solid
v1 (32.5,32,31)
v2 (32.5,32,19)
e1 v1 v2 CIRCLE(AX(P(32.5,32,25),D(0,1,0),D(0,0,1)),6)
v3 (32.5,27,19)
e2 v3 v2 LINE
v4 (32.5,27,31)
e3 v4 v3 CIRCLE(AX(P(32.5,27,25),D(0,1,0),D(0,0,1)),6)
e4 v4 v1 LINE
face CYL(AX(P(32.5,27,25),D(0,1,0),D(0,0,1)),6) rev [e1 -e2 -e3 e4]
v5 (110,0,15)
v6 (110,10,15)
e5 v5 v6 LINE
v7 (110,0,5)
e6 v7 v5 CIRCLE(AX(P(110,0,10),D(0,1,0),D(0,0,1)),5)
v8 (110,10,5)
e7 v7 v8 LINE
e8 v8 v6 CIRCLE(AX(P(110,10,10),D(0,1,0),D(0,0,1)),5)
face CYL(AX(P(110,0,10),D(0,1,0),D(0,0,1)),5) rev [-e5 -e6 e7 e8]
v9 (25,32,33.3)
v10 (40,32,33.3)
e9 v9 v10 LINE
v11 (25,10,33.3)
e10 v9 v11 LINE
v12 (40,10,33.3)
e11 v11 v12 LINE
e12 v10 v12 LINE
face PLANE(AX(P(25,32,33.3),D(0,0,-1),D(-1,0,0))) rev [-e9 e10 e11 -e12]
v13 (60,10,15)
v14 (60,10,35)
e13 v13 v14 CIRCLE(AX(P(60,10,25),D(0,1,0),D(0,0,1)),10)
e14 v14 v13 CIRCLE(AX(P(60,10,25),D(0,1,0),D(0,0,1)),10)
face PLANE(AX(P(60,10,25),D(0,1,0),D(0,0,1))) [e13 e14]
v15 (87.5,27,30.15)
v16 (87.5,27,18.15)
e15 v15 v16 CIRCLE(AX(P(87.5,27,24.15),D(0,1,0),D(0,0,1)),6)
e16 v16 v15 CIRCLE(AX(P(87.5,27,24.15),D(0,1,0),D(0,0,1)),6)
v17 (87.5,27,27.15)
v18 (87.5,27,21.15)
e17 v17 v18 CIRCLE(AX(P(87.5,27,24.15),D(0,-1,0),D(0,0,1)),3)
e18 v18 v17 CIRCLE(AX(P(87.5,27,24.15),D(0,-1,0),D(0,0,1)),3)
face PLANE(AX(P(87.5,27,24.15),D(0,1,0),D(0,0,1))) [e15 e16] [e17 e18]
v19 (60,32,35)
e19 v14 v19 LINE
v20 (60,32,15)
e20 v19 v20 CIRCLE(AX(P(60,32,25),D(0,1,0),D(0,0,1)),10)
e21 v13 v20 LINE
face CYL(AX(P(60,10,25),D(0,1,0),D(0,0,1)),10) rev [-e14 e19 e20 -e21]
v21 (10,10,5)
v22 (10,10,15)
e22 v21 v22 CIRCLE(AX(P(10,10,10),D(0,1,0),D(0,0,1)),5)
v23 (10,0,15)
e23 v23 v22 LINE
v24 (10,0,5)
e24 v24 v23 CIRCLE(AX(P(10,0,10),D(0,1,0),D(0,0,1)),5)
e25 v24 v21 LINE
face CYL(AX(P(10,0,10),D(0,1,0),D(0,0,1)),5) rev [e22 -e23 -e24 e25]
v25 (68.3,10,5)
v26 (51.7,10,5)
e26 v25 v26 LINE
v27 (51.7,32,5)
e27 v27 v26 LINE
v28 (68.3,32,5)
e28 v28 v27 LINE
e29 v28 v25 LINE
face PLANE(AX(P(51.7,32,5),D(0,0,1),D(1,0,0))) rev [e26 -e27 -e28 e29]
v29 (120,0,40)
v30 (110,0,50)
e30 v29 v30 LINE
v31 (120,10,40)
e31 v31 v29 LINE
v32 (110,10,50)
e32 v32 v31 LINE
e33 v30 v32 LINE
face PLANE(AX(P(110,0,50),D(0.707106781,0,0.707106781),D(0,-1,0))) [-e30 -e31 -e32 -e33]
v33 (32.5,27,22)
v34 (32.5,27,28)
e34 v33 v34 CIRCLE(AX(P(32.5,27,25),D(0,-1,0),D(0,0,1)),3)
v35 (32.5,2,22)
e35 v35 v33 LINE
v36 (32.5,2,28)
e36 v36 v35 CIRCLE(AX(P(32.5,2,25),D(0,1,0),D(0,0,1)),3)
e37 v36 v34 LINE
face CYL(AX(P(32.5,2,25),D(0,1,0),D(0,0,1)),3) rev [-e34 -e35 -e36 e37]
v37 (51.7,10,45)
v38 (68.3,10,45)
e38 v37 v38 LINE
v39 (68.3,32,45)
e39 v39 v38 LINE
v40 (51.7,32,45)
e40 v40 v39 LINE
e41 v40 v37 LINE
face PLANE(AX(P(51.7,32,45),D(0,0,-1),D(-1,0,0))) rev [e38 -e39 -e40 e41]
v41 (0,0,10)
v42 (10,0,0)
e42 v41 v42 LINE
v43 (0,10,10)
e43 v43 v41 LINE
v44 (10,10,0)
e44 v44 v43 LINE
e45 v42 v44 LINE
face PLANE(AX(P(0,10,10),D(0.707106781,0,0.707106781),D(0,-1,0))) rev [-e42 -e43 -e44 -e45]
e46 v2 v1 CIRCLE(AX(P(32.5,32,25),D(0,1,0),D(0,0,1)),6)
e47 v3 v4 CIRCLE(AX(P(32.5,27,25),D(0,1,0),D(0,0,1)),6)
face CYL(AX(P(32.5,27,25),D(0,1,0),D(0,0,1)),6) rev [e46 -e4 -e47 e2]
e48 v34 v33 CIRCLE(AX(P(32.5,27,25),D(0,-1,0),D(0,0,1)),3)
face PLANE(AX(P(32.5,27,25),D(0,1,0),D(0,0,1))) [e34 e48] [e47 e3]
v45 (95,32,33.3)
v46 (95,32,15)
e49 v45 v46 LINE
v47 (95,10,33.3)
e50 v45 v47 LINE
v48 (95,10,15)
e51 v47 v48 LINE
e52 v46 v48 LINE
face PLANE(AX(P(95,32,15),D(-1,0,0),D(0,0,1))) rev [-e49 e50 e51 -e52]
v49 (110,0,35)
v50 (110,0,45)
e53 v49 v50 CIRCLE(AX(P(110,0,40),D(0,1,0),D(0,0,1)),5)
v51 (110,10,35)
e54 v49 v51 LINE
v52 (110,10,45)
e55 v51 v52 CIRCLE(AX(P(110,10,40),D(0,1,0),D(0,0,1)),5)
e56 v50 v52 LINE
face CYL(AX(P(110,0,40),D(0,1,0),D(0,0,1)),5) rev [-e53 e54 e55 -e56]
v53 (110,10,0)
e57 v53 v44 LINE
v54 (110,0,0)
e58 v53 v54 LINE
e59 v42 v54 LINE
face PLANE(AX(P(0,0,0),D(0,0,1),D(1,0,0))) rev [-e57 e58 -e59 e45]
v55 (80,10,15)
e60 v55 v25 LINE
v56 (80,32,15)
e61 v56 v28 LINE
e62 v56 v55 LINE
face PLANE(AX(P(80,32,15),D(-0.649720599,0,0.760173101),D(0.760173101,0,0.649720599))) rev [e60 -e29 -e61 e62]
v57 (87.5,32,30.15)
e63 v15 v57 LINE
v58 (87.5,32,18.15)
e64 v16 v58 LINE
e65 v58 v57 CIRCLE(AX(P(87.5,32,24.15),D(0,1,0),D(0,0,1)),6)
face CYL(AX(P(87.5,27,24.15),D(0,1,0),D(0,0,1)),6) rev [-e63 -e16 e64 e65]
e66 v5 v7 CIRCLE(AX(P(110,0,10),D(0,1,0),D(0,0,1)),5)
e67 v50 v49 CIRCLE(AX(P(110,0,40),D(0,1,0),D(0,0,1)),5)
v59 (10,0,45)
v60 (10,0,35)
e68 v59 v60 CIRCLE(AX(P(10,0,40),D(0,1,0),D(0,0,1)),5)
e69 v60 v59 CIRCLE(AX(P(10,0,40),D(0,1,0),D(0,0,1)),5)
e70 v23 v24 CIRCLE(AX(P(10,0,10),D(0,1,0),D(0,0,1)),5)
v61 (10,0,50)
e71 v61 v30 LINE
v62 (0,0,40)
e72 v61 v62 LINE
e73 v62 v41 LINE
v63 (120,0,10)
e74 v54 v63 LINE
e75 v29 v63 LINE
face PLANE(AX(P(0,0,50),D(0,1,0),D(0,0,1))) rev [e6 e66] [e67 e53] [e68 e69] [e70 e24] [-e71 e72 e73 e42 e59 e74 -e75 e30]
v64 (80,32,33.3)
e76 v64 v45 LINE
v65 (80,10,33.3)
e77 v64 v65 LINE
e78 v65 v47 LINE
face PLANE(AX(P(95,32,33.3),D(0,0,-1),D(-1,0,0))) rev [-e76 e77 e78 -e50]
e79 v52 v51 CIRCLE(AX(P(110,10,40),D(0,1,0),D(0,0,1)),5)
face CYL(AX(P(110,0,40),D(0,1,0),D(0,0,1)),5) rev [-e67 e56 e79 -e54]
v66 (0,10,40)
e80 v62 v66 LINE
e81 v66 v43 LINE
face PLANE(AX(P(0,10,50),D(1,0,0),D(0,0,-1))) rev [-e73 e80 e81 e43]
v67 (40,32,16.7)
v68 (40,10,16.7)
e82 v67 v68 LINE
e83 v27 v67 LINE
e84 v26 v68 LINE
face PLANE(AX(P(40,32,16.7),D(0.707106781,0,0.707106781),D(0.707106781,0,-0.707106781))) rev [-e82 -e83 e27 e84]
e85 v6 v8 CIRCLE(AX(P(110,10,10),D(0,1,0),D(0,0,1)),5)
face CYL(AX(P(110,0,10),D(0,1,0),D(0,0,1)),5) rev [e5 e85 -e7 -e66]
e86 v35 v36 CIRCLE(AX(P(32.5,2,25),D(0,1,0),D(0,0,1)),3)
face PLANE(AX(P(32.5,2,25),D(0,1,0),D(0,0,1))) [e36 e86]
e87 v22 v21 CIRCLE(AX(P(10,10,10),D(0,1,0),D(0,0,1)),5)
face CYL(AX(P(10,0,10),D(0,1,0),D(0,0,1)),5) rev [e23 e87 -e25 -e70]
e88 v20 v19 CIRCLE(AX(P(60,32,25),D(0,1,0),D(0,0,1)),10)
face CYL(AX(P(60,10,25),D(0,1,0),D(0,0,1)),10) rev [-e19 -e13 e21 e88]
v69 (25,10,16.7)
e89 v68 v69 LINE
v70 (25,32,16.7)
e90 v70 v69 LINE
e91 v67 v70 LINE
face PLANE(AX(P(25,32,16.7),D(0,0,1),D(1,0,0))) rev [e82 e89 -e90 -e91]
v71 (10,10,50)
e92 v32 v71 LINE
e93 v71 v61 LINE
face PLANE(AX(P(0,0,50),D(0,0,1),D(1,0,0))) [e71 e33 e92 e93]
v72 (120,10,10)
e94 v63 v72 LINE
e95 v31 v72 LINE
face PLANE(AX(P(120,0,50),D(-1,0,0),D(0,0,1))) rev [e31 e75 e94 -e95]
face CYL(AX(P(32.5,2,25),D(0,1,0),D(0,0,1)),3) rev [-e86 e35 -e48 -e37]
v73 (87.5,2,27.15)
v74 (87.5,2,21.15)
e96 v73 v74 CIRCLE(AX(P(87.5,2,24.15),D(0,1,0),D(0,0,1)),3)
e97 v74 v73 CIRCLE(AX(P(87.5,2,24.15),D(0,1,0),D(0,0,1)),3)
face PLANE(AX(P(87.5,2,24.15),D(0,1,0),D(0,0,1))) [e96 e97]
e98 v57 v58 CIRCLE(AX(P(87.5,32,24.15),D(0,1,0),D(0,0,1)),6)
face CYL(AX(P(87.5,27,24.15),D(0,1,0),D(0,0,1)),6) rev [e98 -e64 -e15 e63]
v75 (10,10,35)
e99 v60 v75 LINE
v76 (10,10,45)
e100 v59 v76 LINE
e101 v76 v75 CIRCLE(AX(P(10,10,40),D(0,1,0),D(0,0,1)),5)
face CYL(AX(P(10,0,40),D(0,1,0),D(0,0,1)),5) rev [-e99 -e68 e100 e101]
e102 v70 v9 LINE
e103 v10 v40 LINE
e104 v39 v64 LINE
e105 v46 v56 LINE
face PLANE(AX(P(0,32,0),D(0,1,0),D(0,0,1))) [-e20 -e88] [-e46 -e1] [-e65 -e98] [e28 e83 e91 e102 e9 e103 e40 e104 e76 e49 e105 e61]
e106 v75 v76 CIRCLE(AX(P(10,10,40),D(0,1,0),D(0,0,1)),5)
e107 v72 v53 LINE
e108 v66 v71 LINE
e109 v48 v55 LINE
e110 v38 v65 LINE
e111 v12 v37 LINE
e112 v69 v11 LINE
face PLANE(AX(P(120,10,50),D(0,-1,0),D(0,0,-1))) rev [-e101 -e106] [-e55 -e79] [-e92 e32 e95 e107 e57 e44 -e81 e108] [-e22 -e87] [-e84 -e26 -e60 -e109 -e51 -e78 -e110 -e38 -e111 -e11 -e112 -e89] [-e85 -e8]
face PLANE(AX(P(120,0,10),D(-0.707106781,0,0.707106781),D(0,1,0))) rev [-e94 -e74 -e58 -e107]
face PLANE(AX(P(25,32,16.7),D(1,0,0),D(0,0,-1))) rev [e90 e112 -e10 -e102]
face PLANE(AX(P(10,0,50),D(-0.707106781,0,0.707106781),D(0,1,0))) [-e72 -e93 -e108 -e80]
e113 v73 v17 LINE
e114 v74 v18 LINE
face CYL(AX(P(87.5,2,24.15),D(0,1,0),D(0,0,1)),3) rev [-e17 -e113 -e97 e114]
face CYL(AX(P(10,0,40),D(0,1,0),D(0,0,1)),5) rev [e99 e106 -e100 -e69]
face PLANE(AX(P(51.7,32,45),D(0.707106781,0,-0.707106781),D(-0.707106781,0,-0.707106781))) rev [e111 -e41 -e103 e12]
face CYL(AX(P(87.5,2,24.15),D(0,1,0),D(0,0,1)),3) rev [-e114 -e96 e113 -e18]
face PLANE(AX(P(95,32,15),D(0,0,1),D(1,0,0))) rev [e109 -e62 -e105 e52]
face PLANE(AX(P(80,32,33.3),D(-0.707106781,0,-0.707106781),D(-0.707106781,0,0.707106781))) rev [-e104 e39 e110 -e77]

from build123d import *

# Parameters (mm, degrees)
BASE_PLATE_SKETCH_W        = 120
BASE_PLATE_SKETCH_H        = 10
BASE_PLATE_DEPTH           = 50
MOUNTING_HOLES_SKETCH_R    = 5
MOUNTING_HOLES_4X_10_DEPTH = 131.384048104
CENTER_SUPPORT_DEPTH       = 22
CENTER_BORE_SKETCH_R       = 10
CENTER_BORE_20_DEPTH       = 22
SUPPORT_HOLES_SKETCH_R     = 3
SUPPORT_HOLES_2X_6_DEPTH   = 30
COUNTERBORE_SKETCH_R       = 6
COUNTERBORES_2X_12X5_DEPTH = 5
CORNER_CHAMFERS_10MM_SIZE  = 10


with BuildPart() as part:
    # Base Plate Sketch → Base Plate (new body)
    with BuildSketch(Plane.XY):
        with Locations((60, 5)):
            Rectangle(BASE_PLATE_SKETCH_W, BASE_PLATE_SKETCH_H)
    extrude(amount=BASE_PLATE_DEPTH)

    # Mounting Holes Sketch → Mounting Holes 4xØ10 (cut, through all)
    with BuildSketch(Plane(origin=(0, 10, 0), x_dir=(1, 0, 0), z_dir=(0, 1, 0))):
        with Locations(Location((10, -10, 0), (0, 0, 270))):
            Circle(MOUNTING_HOLES_SKETCH_R)
        with Locations(Location((10, -40, 0), (0, 0, 270))):
            Circle(MOUNTING_HOLES_SKETCH_R)
        with Locations(Location((110, -10, 0), (0, 0, 270))):
            Circle(MOUNTING_HOLES_SKETCH_R)
        with Locations(Location((110, -40, 0), (0, 0, 270))):
            Circle(MOUNTING_HOLES_SKETCH_R)
    extrude(amount=-MOUNTING_HOLES_4X_10_DEPTH, mode=Mode.SUBTRACT)

    # Center Support Sketch → Center Support (add)
    with BuildSketch(Plane(origin=(0, 10, 0), x_dir=(1, 0, 0), z_dir=(0, 1, 0))):
        Polygon((25, -16.7), (40, -16.7), (51.7, -5), (68.3, -5), (80, -15), (95, -15), (95, -33.3), (80, -33.3), (68.3, -45), (51.7, -45), (40, -33.3), (25, -33.3), align=None)
    extrude(amount=CENTER_SUPPORT_DEPTH)

    # Center Bore Sketch → Center Bore Ø20 (cut)
    with BuildSketch(Plane(origin=(0, 32, 0), x_dir=(1, 0, 0), z_dir=(0, 1, 0))):
        with Locations(Location((60, -25, 0), (0, 0, 270))):
            Circle(CENTER_BORE_SKETCH_R)
    extrude(amount=-CENTER_BORE_20_DEPTH, mode=Mode.SUBTRACT)

    # Support Holes Sketch → Support Holes 2xØ6 (cut)
    with BuildSketch(Plane(origin=(0, 32, 0), x_dir=(1, 0, 0), z_dir=(0, 1, 0))):
        with Locations(Location((32.5, -25, 0), (0, 0, 270))):
            Circle(SUPPORT_HOLES_SKETCH_R)
        with Locations(Location((87.5, -24.15, 0), (0, 0, 270))):
            Circle(SUPPORT_HOLES_SKETCH_R)
    extrude(amount=-SUPPORT_HOLES_2X_6_DEPTH, mode=Mode.SUBTRACT)

    # Counterbore Sketch → Counterbores 2xØ12x5 (cut)
    with BuildSketch(Plane(origin=(0, 32, 0), x_dir=(1, 0, 0), z_dir=(0, 1, 0))):
        with Locations(Location((32.5, -25, 0), (0, 0, 270))):
            Circle(COUNTERBORE_SKETCH_R)
        with Locations(Location((87.5, -24.15, 0), (0, 0, 270))):
            Circle(COUNTERBORE_SKETCH_R)
    extrude(amount=-COUNTERBORES_2X_12X5_DEPTH, mode=Mode.SUBTRACT)

    # Corner Chamfers 10mm
    corner_chamfers_10mm_edges = [part.edges().sort_by_distance(p)[0] for p in [
        (120, 5, 50),
        (0, 5, 50),
        (120, 5, 0),
        (0, 5, 0),
    ]]
    chamfer(corner_chamfers_10mm_edges, length=CORNER_CHAMFERS_10MM_SIZE)


solid = part.part
